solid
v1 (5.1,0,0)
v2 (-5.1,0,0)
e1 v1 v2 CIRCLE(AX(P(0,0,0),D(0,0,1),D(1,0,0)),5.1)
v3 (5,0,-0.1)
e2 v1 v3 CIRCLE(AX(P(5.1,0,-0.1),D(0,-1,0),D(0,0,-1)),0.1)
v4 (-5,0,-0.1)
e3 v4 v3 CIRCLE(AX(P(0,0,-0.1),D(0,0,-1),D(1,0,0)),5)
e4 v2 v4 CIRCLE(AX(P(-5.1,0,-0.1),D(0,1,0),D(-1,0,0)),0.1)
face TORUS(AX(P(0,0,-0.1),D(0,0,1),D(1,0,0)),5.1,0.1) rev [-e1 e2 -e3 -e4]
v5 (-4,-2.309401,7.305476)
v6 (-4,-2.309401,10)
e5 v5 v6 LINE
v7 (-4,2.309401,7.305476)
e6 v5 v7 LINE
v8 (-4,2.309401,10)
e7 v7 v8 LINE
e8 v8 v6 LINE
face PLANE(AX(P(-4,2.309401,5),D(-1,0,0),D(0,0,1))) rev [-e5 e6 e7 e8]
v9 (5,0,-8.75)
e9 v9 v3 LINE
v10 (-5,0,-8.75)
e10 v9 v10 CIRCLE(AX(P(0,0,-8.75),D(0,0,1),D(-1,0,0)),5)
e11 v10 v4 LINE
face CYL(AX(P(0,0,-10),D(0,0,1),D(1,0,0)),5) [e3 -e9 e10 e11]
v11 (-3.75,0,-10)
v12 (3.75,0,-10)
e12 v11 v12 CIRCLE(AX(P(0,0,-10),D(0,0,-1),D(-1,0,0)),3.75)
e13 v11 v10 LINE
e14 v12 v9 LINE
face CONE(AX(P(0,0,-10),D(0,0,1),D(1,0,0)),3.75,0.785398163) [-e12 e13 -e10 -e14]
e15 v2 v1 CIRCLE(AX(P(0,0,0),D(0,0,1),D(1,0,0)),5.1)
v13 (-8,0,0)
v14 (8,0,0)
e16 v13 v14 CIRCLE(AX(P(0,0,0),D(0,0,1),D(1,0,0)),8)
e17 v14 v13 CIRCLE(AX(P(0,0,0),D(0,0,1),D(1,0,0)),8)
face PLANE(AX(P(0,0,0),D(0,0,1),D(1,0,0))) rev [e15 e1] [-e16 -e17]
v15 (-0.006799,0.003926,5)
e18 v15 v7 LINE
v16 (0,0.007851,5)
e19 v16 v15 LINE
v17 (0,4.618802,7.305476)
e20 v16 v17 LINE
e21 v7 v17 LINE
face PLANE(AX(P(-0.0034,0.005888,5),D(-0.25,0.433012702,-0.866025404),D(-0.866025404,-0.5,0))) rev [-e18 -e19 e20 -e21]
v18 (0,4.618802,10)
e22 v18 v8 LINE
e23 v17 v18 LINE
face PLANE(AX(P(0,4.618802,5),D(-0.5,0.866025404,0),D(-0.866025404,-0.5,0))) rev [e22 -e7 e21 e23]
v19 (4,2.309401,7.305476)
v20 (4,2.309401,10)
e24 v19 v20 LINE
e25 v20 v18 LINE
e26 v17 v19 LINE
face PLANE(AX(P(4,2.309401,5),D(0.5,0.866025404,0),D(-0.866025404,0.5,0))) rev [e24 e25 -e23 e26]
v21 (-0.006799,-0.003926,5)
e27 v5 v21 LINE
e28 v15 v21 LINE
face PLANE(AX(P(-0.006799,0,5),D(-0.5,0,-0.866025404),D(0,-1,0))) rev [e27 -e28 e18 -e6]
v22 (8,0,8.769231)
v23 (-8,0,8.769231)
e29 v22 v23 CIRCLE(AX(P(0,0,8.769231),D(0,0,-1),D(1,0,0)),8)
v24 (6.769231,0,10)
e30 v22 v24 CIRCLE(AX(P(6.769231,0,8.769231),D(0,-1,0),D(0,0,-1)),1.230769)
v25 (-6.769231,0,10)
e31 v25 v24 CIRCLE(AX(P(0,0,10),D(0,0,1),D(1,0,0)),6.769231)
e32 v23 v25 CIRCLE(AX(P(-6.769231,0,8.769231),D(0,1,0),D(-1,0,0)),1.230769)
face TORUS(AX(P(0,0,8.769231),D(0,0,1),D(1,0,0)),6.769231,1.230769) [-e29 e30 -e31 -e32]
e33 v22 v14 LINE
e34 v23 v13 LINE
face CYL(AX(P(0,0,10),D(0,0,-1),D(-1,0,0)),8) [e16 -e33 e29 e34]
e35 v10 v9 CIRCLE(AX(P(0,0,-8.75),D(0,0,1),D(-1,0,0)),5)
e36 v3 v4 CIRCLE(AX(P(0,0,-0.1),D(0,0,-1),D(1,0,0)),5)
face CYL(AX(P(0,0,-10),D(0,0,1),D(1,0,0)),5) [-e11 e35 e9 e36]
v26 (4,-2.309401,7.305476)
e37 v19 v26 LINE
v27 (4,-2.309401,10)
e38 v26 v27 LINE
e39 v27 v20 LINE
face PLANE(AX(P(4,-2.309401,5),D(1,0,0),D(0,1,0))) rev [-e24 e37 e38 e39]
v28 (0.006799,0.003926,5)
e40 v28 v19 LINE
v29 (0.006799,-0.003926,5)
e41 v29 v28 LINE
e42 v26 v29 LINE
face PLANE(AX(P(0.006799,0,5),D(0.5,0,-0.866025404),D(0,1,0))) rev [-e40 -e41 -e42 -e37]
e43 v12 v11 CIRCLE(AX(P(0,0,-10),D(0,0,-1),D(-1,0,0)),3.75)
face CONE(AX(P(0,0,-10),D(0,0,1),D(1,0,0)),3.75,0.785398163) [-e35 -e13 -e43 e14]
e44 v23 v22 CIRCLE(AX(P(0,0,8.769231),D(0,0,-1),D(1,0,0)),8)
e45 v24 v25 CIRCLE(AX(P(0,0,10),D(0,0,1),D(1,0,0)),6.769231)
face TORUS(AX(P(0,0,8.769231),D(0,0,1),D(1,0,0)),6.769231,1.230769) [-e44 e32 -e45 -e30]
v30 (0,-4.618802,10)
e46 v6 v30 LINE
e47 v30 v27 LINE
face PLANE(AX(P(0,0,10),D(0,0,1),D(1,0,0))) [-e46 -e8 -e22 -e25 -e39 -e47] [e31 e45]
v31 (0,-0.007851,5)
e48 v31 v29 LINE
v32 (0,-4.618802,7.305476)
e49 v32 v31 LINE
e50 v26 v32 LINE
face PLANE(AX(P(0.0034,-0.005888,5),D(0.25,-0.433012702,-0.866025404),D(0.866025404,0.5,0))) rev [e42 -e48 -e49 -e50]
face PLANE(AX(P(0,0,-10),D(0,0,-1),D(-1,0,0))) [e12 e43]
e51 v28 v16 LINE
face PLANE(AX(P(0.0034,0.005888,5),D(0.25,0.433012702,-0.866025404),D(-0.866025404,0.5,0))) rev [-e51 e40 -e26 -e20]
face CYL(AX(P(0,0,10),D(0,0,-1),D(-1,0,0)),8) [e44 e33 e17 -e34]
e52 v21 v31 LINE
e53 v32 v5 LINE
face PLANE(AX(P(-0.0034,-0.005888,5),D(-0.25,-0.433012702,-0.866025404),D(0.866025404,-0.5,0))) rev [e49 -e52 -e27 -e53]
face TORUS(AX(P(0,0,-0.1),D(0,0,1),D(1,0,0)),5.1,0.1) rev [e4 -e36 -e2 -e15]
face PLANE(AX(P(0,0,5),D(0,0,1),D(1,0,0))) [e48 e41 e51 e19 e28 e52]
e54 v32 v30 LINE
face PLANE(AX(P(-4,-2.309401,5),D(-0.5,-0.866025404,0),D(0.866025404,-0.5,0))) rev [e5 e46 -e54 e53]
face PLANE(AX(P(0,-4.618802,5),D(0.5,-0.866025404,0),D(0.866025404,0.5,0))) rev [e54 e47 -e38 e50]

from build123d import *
from OCP.BRepFilletAPI import BRepFilletAPI_MakeChamfer

# Parameters (mm, degrees)
SKETCH_1_R          = 8
EXTRUDE_1_DEPTH     = 10
CUT_EXTRUDE_1_DEPTH = 5
SKETCH_3_R          = 5
EXTRUDE_2_DEPTH     = 10
CHAMFER_1_SIZE      = 1.25
FILLET_1_R          = 1.230769231
CHAMFER_2_SIZE      = 2.305475504
CHAMFER_2_SIZE2     = 3.993200709
FILLET_2_R          = 0.1


with BuildPart() as part:
    # 草图1 → 凸台-拉伸1 (new body)
    with BuildSketch(Plane.XY):
        Circle(SKETCH_1_R)
    extrude(amount=EXTRUDE_1_DEPTH)

    # 草图2 → 切除-拉伸1 (cut)
    with BuildSketch(Plane.XY.offset(10)):
        Polygon((4, 2.309401077), (0, 4.618802154), (-4, 2.309401077), (-4, -2.309401077), (0, -4.618802154), (4, -2.309401077), align=None)
    extrude(amount=-CUT_EXTRUDE_1_DEPTH, mode=Mode.SUBTRACT)

    # 草图3 → 凸台-拉伸2 (add)
    with BuildSketch(Plane(origin=(0, 0, 0), x_dir=(-1, 0, 0), z_dir=(0, 0, -1))):
        with Locations(Location((0, 0, 0), (0, 0, 180))):
            Circle(SKETCH_3_R)
    extrude(amount=EXTRUDE_2_DEPTH)

    # 倒角1
    chamfer_1_edges = [part.edges().sort_by_distance(p)[0] for p in [
        (-5, 0, -10),
    ]]
    chamfer(chamfer_1_edges, length=CHAMFER_1_SIZE)

    # 圆角1
    fillet_1_edges = [part.edges().sort_by_distance(p)[0] for p in [
        (-8, 0, 10),
    ]]
    fillet(fillet_1_edges, radius=FILLET_1_R)

    # 倒角2: one chamfer whose edges measure the first distance from different faces: ONE call of the kernel's chamfer builder (chamfer() names one face for all edges)
    chamfer_2_edges_1 = [part.edges().sort_by_distance(p)[0] for p in [
        (2, 3.464101615, 5),
    ]]
    chamfer_2_side_1 = [part.faces().sort_by_distance(p)[0] for p in [
        (2, 3.464101615, 7.5),
    ]]
    chamfer_2_edges_2 = [part.edges().sort_by_distance(p)[0] for p in [
        (4, 0, 5),
    ]]
    chamfer_2_side_2 = [part.faces().sort_by_distance(p)[0] for p in [
        (4, 0, 7.5),
    ]]
    chamfer_2_edges_3 = [part.edges().sort_by_distance(p)[0] for p in [
        (2, -3.464101615, 5),
    ]]
    chamfer_2_side_3 = [part.faces().sort_by_distance(p)[0] for p in [
        (2, -3.464101615, 7.5),
    ]]
    chamfer_2_edges_4 = [part.edges().sort_by_distance(p)[0] for p in [
        (-2, -3.464101615, 5),
    ]]
    chamfer_2_side_4 = [part.faces().sort_by_distance(p)[0] for p in [
        (-2, -3.464101615, 7.5),
    ]]
    chamfer_2_edges_5 = [part.edges().sort_by_distance(p)[0] for p in [
        (-4, 0, 5),
    ]]
    chamfer_2_side_5 = [part.faces().sort_by_distance(p)[0] for p in [
        (-4, 0, 7.5),
    ]]
    chamfer_2_edges_6 = [part.edges().sort_by_distance(p)[0] for p in [
        (-2, 3.464101615, 5),
    ]]
    chamfer_2_side_6 = [part.faces().sort_by_distance(p)[0] for p in [
        (-2, 3.464101615, 7.5),
    ]]
    chamfer_2 = BRepFilletAPI_MakeChamfer(part.part.solid().wrapped)
    for e in chamfer_2_edges_1:
        chamfer_2.Add(CHAMFER_2_SIZE, CHAMFER_2_SIZE2, e.wrapped, chamfer_2_side_1[0].wrapped)  # the first distance lies on this face
    for e in chamfer_2_edges_2:
        chamfer_2.Add(CHAMFER_2_SIZE, CHAMFER_2_SIZE2, e.wrapped, chamfer_2_side_2[0].wrapped)  # the first distance lies on this face
    for e in chamfer_2_edges_3:
        chamfer_2.Add(CHAMFER_2_SIZE, CHAMFER_2_SIZE2, e.wrapped, chamfer_2_side_3[0].wrapped)  # the first distance lies on this face
    for e in chamfer_2_edges_4:
        chamfer_2.Add(CHAMFER_2_SIZE, CHAMFER_2_SIZE2, e.wrapped, chamfer_2_side_4[0].wrapped)  # the first distance lies on this face
    for e in chamfer_2_edges_5:
        chamfer_2.Add(CHAMFER_2_SIZE, CHAMFER_2_SIZE2, e.wrapped, chamfer_2_side_5[0].wrapped)  # the first distance lies on this face
    for e in chamfer_2_edges_6:
        chamfer_2.Add(CHAMFER_2_SIZE, CHAMFER_2_SIZE2, e.wrapped, chamfer_2_side_6[0].wrapped)  # the first distance lies on this face
    add(Compound.cast(chamfer_2.Shape()), mode=Mode.REPLACE)

    # 圆角2
    fillet_2_edges = [part.edges().sort_by_distance(p)[0] for p in [
        (-5, 0, 0),
    ]]
    fillet(fillet_2_edges, radius=FILLET_2_R)


solid = part.part
